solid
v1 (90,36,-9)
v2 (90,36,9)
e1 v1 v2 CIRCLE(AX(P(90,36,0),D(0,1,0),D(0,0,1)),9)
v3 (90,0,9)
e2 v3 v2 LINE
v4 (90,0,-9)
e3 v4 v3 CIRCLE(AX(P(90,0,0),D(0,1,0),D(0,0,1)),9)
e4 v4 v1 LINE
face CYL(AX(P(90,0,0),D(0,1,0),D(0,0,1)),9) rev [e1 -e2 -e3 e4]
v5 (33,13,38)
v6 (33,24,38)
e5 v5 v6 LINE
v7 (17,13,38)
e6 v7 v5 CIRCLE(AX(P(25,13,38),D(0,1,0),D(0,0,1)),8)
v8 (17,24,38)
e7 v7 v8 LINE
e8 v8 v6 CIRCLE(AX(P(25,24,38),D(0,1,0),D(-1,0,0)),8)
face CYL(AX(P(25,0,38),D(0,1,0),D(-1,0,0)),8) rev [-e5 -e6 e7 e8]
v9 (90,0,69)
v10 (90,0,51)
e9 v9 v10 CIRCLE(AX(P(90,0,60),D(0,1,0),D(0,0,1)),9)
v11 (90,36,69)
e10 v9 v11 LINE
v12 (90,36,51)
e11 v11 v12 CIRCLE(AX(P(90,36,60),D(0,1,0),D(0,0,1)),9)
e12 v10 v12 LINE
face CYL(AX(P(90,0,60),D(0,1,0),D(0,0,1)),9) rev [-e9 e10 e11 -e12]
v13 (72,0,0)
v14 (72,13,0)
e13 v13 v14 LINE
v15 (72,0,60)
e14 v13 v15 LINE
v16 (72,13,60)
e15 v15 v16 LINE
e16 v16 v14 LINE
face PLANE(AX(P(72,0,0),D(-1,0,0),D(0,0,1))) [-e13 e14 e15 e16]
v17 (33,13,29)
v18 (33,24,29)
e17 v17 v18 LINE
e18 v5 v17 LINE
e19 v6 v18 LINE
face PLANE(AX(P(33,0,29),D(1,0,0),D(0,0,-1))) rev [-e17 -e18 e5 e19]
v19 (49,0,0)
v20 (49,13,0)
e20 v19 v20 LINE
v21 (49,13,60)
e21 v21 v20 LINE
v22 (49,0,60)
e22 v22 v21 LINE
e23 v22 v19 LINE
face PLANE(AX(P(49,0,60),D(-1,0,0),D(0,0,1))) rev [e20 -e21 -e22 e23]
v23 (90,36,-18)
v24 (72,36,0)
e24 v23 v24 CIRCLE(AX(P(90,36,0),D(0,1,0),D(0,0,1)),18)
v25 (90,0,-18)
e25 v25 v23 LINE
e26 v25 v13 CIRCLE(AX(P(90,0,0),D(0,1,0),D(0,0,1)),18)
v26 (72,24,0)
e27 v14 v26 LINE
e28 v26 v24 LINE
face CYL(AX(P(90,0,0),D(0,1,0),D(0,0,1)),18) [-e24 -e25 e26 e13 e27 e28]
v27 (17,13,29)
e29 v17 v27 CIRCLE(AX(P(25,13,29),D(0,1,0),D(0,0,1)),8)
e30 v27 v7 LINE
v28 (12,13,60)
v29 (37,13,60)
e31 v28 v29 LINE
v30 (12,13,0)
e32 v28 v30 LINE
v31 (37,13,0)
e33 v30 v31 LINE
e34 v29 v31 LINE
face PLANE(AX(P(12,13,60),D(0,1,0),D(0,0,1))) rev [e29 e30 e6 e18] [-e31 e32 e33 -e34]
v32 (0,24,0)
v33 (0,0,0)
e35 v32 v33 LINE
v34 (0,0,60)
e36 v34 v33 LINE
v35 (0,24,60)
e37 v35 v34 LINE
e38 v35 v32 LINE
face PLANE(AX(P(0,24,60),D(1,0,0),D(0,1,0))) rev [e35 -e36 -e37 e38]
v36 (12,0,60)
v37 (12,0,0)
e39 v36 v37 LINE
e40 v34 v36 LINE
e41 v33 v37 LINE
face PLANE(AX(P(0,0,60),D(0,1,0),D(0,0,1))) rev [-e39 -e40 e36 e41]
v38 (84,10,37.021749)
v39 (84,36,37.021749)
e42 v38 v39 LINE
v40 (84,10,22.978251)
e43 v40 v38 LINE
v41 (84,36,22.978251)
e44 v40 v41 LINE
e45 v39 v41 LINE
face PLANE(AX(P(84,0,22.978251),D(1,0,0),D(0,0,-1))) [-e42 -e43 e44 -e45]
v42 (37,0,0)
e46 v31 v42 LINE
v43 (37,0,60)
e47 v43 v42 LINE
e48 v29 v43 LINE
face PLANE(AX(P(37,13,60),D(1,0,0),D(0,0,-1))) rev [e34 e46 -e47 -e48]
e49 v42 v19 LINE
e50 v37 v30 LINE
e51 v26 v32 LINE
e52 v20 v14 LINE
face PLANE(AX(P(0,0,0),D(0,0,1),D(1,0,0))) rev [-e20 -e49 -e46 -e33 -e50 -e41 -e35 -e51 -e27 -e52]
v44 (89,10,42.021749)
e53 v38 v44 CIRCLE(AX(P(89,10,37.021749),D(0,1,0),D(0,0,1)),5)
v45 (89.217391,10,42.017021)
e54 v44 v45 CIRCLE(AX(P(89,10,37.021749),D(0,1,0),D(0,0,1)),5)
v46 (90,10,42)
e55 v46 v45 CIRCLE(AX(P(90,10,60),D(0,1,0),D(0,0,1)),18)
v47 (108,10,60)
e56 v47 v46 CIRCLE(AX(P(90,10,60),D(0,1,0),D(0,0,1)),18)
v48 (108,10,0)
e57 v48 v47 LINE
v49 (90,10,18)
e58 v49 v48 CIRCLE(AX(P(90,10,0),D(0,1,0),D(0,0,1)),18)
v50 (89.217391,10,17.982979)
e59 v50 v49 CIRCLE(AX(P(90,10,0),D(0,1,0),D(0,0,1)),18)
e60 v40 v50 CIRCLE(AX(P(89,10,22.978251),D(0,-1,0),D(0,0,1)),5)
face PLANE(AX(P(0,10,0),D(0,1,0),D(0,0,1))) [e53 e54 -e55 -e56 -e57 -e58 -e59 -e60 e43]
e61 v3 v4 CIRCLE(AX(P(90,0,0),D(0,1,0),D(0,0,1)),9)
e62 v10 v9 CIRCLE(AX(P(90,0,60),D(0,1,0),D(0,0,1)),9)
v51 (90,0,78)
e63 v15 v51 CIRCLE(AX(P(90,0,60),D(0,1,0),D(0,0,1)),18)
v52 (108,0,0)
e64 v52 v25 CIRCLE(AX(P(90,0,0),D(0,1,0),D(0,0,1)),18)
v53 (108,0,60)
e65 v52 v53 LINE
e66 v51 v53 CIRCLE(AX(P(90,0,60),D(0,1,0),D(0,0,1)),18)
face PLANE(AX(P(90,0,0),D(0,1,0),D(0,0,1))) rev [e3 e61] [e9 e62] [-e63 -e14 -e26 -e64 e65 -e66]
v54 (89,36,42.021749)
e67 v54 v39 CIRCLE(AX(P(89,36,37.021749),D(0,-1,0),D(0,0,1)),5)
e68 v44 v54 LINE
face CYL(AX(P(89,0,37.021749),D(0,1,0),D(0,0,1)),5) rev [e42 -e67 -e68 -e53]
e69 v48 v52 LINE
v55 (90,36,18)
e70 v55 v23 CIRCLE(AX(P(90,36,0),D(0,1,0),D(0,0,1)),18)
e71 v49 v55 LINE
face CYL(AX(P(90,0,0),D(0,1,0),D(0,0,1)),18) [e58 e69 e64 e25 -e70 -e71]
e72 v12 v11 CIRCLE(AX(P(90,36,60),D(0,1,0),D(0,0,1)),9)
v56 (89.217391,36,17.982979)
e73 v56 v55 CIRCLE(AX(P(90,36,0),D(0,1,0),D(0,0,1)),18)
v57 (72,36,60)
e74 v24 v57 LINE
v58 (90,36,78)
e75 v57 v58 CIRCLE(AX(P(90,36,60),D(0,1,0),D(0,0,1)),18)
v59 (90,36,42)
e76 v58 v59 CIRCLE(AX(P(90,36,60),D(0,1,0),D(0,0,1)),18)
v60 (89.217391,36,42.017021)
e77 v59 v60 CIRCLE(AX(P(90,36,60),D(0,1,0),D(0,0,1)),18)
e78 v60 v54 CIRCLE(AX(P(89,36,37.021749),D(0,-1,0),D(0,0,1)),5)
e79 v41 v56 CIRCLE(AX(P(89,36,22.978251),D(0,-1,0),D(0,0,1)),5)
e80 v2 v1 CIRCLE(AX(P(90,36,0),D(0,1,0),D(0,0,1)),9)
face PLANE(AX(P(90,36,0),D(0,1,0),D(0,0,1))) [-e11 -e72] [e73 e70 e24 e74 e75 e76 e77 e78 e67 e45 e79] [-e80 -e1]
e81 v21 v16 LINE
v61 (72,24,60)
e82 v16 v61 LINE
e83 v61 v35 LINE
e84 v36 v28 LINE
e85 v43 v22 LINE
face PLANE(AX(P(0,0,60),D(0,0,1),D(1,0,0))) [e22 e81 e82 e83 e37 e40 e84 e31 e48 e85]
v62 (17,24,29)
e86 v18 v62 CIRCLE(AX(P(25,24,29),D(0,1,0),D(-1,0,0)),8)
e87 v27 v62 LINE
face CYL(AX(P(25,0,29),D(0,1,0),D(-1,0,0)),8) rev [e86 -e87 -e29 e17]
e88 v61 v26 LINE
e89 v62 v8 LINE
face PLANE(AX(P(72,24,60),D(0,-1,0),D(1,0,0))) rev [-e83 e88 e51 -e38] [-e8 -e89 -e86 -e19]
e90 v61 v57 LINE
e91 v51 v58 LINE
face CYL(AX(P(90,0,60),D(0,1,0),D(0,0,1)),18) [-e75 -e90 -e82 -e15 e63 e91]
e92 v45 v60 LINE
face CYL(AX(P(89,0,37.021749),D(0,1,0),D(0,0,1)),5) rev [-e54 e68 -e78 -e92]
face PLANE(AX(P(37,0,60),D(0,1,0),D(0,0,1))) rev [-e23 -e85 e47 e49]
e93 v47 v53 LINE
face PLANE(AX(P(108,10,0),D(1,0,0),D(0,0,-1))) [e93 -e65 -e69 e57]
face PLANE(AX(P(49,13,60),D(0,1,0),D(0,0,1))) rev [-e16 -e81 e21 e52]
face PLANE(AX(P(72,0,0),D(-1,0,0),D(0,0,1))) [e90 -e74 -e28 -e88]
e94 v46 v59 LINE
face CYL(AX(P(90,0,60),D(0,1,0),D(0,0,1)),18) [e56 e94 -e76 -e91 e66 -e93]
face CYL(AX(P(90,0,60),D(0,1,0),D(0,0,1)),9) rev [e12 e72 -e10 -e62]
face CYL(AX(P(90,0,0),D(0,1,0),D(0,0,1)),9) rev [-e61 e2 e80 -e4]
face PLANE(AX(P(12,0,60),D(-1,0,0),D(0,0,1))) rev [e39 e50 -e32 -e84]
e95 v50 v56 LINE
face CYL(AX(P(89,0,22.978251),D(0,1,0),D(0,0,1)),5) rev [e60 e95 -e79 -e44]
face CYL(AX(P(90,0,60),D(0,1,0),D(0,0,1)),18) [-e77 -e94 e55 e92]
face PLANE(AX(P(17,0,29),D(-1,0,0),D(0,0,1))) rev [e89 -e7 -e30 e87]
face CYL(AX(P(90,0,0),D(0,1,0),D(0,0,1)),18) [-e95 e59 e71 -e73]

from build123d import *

# Parameters (mm, degrees)
BASE_BLOCK_DEPTH          = 60
TWIN_LUG_PROFILE_SKETCH_R = 9
TWIN_LUGS_DEPTH           = 36
LUG_START                 = 10
LUG_WEB_DEPTH             = 10
MOUNTING_SLOT_9MM_DEPTH   = 136.366170072


with BuildPart() as part:
    # Base Block Profile Sketch → Base Block (new body)
    with BuildSketch(Plane.XY):
        Polygon((0, 0), (12, 0), (12, 13), (37, 13), (37, 0), (49, 0), (49, 13), (72, 13), (72, 24), (0, 24), align=None)
    extrude(amount=BASE_BLOCK_DEPTH)

    # Twin Lug Profile Sketch → Twin Lugs (add)
    with BuildSketch(Plane(origin=(0, 36, 0), x_dir=(1, 0, 0), z_dir=(0, 1, 0))):
        with BuildLine():
            Line((72, 0), (72, -60))
            ThreePointArc((72, -60), (103.001672133, -72.448153347), (89.217391304, -42.01702128))
            ThreePointArc((89.217391304, -42.01702128), (85.542179626, -40.633325006), (84, -37.021749414))
            Line((84, -37.021749414), (84, -22.978250586))
            ThreePointArc((84, -22.978250586), (85.542179626, -19.366674994), (89.217391304, -17.98297872))
            ThreePointArc((89.217391304, -17.98297872), (103.001672133, 12.448153347), (72, 0))
        make_face()
        with Locations(Location((90, 0, 0), (0, 0, 270))):
            Circle(TWIN_LUG_PROFILE_SKETCH_R, mode=Mode.SUBTRACT)
        with Locations(Location((90, -60, 0), (0, 0, 270))):
            Circle(TWIN_LUG_PROFILE_SKETCH_R, mode=Mode.SUBTRACT)
    extrude(amount=-TWIN_LUGS_DEPTH)

    # Lug Web Profile Sketch → Lug Web (add)
    with BuildSketch(Plane(origin=(0, 0, 0), x_dir=(1, 0, 0), z_dir=(0, 1, 0)).offset(LUG_START)):
        with BuildLine():
            Line((108, -60), (108, 0))
            ThreePointArc((108, 0), (102.448153347, -13.001672133), (89.217391304, -17.98297872))
            ThreePointArc((89.217391304, -17.98297872), (85.542179626, -19.366674994), (84, -22.978250586))
            Line((84, -22.978250586), (84, -37.021749414))
            ThreePointArc((84, -37.021749414), (85.241609163, -40.399518098), (88.429875668, -42.068611053))
            ThreePointArc((88.429875668, -42.068611053), (89.214188653, -42.017160944), (90, -42))
            ThreePointArc((90, -42), (102.727922061, -47.272077939), (108, -60))
        make_face()
    extrude(amount=-LUG_WEB_DEPTH)

    # Mounting Slot Sketch → Mounting Slot 9mm (cut, through all)
    with BuildSketch(Plane(origin=(0, 24, 0), x_dir=(1, 0, 0), z_dir=(0, 1, 0))):
        with BuildLine():
            Line((33, -29), (33, -38))
            ThreePointArc((33, -38), (25, -46), (17, -38))
            Line((17, -38), (17, -29))
            ThreePointArc((17, -29), (25, -21), (33, -29))
        make_face()
    extrude(amount=-MOUNTING_SLOT_9MM_DEPTH, mode=Mode.SUBTRACT)


solid = part.part
